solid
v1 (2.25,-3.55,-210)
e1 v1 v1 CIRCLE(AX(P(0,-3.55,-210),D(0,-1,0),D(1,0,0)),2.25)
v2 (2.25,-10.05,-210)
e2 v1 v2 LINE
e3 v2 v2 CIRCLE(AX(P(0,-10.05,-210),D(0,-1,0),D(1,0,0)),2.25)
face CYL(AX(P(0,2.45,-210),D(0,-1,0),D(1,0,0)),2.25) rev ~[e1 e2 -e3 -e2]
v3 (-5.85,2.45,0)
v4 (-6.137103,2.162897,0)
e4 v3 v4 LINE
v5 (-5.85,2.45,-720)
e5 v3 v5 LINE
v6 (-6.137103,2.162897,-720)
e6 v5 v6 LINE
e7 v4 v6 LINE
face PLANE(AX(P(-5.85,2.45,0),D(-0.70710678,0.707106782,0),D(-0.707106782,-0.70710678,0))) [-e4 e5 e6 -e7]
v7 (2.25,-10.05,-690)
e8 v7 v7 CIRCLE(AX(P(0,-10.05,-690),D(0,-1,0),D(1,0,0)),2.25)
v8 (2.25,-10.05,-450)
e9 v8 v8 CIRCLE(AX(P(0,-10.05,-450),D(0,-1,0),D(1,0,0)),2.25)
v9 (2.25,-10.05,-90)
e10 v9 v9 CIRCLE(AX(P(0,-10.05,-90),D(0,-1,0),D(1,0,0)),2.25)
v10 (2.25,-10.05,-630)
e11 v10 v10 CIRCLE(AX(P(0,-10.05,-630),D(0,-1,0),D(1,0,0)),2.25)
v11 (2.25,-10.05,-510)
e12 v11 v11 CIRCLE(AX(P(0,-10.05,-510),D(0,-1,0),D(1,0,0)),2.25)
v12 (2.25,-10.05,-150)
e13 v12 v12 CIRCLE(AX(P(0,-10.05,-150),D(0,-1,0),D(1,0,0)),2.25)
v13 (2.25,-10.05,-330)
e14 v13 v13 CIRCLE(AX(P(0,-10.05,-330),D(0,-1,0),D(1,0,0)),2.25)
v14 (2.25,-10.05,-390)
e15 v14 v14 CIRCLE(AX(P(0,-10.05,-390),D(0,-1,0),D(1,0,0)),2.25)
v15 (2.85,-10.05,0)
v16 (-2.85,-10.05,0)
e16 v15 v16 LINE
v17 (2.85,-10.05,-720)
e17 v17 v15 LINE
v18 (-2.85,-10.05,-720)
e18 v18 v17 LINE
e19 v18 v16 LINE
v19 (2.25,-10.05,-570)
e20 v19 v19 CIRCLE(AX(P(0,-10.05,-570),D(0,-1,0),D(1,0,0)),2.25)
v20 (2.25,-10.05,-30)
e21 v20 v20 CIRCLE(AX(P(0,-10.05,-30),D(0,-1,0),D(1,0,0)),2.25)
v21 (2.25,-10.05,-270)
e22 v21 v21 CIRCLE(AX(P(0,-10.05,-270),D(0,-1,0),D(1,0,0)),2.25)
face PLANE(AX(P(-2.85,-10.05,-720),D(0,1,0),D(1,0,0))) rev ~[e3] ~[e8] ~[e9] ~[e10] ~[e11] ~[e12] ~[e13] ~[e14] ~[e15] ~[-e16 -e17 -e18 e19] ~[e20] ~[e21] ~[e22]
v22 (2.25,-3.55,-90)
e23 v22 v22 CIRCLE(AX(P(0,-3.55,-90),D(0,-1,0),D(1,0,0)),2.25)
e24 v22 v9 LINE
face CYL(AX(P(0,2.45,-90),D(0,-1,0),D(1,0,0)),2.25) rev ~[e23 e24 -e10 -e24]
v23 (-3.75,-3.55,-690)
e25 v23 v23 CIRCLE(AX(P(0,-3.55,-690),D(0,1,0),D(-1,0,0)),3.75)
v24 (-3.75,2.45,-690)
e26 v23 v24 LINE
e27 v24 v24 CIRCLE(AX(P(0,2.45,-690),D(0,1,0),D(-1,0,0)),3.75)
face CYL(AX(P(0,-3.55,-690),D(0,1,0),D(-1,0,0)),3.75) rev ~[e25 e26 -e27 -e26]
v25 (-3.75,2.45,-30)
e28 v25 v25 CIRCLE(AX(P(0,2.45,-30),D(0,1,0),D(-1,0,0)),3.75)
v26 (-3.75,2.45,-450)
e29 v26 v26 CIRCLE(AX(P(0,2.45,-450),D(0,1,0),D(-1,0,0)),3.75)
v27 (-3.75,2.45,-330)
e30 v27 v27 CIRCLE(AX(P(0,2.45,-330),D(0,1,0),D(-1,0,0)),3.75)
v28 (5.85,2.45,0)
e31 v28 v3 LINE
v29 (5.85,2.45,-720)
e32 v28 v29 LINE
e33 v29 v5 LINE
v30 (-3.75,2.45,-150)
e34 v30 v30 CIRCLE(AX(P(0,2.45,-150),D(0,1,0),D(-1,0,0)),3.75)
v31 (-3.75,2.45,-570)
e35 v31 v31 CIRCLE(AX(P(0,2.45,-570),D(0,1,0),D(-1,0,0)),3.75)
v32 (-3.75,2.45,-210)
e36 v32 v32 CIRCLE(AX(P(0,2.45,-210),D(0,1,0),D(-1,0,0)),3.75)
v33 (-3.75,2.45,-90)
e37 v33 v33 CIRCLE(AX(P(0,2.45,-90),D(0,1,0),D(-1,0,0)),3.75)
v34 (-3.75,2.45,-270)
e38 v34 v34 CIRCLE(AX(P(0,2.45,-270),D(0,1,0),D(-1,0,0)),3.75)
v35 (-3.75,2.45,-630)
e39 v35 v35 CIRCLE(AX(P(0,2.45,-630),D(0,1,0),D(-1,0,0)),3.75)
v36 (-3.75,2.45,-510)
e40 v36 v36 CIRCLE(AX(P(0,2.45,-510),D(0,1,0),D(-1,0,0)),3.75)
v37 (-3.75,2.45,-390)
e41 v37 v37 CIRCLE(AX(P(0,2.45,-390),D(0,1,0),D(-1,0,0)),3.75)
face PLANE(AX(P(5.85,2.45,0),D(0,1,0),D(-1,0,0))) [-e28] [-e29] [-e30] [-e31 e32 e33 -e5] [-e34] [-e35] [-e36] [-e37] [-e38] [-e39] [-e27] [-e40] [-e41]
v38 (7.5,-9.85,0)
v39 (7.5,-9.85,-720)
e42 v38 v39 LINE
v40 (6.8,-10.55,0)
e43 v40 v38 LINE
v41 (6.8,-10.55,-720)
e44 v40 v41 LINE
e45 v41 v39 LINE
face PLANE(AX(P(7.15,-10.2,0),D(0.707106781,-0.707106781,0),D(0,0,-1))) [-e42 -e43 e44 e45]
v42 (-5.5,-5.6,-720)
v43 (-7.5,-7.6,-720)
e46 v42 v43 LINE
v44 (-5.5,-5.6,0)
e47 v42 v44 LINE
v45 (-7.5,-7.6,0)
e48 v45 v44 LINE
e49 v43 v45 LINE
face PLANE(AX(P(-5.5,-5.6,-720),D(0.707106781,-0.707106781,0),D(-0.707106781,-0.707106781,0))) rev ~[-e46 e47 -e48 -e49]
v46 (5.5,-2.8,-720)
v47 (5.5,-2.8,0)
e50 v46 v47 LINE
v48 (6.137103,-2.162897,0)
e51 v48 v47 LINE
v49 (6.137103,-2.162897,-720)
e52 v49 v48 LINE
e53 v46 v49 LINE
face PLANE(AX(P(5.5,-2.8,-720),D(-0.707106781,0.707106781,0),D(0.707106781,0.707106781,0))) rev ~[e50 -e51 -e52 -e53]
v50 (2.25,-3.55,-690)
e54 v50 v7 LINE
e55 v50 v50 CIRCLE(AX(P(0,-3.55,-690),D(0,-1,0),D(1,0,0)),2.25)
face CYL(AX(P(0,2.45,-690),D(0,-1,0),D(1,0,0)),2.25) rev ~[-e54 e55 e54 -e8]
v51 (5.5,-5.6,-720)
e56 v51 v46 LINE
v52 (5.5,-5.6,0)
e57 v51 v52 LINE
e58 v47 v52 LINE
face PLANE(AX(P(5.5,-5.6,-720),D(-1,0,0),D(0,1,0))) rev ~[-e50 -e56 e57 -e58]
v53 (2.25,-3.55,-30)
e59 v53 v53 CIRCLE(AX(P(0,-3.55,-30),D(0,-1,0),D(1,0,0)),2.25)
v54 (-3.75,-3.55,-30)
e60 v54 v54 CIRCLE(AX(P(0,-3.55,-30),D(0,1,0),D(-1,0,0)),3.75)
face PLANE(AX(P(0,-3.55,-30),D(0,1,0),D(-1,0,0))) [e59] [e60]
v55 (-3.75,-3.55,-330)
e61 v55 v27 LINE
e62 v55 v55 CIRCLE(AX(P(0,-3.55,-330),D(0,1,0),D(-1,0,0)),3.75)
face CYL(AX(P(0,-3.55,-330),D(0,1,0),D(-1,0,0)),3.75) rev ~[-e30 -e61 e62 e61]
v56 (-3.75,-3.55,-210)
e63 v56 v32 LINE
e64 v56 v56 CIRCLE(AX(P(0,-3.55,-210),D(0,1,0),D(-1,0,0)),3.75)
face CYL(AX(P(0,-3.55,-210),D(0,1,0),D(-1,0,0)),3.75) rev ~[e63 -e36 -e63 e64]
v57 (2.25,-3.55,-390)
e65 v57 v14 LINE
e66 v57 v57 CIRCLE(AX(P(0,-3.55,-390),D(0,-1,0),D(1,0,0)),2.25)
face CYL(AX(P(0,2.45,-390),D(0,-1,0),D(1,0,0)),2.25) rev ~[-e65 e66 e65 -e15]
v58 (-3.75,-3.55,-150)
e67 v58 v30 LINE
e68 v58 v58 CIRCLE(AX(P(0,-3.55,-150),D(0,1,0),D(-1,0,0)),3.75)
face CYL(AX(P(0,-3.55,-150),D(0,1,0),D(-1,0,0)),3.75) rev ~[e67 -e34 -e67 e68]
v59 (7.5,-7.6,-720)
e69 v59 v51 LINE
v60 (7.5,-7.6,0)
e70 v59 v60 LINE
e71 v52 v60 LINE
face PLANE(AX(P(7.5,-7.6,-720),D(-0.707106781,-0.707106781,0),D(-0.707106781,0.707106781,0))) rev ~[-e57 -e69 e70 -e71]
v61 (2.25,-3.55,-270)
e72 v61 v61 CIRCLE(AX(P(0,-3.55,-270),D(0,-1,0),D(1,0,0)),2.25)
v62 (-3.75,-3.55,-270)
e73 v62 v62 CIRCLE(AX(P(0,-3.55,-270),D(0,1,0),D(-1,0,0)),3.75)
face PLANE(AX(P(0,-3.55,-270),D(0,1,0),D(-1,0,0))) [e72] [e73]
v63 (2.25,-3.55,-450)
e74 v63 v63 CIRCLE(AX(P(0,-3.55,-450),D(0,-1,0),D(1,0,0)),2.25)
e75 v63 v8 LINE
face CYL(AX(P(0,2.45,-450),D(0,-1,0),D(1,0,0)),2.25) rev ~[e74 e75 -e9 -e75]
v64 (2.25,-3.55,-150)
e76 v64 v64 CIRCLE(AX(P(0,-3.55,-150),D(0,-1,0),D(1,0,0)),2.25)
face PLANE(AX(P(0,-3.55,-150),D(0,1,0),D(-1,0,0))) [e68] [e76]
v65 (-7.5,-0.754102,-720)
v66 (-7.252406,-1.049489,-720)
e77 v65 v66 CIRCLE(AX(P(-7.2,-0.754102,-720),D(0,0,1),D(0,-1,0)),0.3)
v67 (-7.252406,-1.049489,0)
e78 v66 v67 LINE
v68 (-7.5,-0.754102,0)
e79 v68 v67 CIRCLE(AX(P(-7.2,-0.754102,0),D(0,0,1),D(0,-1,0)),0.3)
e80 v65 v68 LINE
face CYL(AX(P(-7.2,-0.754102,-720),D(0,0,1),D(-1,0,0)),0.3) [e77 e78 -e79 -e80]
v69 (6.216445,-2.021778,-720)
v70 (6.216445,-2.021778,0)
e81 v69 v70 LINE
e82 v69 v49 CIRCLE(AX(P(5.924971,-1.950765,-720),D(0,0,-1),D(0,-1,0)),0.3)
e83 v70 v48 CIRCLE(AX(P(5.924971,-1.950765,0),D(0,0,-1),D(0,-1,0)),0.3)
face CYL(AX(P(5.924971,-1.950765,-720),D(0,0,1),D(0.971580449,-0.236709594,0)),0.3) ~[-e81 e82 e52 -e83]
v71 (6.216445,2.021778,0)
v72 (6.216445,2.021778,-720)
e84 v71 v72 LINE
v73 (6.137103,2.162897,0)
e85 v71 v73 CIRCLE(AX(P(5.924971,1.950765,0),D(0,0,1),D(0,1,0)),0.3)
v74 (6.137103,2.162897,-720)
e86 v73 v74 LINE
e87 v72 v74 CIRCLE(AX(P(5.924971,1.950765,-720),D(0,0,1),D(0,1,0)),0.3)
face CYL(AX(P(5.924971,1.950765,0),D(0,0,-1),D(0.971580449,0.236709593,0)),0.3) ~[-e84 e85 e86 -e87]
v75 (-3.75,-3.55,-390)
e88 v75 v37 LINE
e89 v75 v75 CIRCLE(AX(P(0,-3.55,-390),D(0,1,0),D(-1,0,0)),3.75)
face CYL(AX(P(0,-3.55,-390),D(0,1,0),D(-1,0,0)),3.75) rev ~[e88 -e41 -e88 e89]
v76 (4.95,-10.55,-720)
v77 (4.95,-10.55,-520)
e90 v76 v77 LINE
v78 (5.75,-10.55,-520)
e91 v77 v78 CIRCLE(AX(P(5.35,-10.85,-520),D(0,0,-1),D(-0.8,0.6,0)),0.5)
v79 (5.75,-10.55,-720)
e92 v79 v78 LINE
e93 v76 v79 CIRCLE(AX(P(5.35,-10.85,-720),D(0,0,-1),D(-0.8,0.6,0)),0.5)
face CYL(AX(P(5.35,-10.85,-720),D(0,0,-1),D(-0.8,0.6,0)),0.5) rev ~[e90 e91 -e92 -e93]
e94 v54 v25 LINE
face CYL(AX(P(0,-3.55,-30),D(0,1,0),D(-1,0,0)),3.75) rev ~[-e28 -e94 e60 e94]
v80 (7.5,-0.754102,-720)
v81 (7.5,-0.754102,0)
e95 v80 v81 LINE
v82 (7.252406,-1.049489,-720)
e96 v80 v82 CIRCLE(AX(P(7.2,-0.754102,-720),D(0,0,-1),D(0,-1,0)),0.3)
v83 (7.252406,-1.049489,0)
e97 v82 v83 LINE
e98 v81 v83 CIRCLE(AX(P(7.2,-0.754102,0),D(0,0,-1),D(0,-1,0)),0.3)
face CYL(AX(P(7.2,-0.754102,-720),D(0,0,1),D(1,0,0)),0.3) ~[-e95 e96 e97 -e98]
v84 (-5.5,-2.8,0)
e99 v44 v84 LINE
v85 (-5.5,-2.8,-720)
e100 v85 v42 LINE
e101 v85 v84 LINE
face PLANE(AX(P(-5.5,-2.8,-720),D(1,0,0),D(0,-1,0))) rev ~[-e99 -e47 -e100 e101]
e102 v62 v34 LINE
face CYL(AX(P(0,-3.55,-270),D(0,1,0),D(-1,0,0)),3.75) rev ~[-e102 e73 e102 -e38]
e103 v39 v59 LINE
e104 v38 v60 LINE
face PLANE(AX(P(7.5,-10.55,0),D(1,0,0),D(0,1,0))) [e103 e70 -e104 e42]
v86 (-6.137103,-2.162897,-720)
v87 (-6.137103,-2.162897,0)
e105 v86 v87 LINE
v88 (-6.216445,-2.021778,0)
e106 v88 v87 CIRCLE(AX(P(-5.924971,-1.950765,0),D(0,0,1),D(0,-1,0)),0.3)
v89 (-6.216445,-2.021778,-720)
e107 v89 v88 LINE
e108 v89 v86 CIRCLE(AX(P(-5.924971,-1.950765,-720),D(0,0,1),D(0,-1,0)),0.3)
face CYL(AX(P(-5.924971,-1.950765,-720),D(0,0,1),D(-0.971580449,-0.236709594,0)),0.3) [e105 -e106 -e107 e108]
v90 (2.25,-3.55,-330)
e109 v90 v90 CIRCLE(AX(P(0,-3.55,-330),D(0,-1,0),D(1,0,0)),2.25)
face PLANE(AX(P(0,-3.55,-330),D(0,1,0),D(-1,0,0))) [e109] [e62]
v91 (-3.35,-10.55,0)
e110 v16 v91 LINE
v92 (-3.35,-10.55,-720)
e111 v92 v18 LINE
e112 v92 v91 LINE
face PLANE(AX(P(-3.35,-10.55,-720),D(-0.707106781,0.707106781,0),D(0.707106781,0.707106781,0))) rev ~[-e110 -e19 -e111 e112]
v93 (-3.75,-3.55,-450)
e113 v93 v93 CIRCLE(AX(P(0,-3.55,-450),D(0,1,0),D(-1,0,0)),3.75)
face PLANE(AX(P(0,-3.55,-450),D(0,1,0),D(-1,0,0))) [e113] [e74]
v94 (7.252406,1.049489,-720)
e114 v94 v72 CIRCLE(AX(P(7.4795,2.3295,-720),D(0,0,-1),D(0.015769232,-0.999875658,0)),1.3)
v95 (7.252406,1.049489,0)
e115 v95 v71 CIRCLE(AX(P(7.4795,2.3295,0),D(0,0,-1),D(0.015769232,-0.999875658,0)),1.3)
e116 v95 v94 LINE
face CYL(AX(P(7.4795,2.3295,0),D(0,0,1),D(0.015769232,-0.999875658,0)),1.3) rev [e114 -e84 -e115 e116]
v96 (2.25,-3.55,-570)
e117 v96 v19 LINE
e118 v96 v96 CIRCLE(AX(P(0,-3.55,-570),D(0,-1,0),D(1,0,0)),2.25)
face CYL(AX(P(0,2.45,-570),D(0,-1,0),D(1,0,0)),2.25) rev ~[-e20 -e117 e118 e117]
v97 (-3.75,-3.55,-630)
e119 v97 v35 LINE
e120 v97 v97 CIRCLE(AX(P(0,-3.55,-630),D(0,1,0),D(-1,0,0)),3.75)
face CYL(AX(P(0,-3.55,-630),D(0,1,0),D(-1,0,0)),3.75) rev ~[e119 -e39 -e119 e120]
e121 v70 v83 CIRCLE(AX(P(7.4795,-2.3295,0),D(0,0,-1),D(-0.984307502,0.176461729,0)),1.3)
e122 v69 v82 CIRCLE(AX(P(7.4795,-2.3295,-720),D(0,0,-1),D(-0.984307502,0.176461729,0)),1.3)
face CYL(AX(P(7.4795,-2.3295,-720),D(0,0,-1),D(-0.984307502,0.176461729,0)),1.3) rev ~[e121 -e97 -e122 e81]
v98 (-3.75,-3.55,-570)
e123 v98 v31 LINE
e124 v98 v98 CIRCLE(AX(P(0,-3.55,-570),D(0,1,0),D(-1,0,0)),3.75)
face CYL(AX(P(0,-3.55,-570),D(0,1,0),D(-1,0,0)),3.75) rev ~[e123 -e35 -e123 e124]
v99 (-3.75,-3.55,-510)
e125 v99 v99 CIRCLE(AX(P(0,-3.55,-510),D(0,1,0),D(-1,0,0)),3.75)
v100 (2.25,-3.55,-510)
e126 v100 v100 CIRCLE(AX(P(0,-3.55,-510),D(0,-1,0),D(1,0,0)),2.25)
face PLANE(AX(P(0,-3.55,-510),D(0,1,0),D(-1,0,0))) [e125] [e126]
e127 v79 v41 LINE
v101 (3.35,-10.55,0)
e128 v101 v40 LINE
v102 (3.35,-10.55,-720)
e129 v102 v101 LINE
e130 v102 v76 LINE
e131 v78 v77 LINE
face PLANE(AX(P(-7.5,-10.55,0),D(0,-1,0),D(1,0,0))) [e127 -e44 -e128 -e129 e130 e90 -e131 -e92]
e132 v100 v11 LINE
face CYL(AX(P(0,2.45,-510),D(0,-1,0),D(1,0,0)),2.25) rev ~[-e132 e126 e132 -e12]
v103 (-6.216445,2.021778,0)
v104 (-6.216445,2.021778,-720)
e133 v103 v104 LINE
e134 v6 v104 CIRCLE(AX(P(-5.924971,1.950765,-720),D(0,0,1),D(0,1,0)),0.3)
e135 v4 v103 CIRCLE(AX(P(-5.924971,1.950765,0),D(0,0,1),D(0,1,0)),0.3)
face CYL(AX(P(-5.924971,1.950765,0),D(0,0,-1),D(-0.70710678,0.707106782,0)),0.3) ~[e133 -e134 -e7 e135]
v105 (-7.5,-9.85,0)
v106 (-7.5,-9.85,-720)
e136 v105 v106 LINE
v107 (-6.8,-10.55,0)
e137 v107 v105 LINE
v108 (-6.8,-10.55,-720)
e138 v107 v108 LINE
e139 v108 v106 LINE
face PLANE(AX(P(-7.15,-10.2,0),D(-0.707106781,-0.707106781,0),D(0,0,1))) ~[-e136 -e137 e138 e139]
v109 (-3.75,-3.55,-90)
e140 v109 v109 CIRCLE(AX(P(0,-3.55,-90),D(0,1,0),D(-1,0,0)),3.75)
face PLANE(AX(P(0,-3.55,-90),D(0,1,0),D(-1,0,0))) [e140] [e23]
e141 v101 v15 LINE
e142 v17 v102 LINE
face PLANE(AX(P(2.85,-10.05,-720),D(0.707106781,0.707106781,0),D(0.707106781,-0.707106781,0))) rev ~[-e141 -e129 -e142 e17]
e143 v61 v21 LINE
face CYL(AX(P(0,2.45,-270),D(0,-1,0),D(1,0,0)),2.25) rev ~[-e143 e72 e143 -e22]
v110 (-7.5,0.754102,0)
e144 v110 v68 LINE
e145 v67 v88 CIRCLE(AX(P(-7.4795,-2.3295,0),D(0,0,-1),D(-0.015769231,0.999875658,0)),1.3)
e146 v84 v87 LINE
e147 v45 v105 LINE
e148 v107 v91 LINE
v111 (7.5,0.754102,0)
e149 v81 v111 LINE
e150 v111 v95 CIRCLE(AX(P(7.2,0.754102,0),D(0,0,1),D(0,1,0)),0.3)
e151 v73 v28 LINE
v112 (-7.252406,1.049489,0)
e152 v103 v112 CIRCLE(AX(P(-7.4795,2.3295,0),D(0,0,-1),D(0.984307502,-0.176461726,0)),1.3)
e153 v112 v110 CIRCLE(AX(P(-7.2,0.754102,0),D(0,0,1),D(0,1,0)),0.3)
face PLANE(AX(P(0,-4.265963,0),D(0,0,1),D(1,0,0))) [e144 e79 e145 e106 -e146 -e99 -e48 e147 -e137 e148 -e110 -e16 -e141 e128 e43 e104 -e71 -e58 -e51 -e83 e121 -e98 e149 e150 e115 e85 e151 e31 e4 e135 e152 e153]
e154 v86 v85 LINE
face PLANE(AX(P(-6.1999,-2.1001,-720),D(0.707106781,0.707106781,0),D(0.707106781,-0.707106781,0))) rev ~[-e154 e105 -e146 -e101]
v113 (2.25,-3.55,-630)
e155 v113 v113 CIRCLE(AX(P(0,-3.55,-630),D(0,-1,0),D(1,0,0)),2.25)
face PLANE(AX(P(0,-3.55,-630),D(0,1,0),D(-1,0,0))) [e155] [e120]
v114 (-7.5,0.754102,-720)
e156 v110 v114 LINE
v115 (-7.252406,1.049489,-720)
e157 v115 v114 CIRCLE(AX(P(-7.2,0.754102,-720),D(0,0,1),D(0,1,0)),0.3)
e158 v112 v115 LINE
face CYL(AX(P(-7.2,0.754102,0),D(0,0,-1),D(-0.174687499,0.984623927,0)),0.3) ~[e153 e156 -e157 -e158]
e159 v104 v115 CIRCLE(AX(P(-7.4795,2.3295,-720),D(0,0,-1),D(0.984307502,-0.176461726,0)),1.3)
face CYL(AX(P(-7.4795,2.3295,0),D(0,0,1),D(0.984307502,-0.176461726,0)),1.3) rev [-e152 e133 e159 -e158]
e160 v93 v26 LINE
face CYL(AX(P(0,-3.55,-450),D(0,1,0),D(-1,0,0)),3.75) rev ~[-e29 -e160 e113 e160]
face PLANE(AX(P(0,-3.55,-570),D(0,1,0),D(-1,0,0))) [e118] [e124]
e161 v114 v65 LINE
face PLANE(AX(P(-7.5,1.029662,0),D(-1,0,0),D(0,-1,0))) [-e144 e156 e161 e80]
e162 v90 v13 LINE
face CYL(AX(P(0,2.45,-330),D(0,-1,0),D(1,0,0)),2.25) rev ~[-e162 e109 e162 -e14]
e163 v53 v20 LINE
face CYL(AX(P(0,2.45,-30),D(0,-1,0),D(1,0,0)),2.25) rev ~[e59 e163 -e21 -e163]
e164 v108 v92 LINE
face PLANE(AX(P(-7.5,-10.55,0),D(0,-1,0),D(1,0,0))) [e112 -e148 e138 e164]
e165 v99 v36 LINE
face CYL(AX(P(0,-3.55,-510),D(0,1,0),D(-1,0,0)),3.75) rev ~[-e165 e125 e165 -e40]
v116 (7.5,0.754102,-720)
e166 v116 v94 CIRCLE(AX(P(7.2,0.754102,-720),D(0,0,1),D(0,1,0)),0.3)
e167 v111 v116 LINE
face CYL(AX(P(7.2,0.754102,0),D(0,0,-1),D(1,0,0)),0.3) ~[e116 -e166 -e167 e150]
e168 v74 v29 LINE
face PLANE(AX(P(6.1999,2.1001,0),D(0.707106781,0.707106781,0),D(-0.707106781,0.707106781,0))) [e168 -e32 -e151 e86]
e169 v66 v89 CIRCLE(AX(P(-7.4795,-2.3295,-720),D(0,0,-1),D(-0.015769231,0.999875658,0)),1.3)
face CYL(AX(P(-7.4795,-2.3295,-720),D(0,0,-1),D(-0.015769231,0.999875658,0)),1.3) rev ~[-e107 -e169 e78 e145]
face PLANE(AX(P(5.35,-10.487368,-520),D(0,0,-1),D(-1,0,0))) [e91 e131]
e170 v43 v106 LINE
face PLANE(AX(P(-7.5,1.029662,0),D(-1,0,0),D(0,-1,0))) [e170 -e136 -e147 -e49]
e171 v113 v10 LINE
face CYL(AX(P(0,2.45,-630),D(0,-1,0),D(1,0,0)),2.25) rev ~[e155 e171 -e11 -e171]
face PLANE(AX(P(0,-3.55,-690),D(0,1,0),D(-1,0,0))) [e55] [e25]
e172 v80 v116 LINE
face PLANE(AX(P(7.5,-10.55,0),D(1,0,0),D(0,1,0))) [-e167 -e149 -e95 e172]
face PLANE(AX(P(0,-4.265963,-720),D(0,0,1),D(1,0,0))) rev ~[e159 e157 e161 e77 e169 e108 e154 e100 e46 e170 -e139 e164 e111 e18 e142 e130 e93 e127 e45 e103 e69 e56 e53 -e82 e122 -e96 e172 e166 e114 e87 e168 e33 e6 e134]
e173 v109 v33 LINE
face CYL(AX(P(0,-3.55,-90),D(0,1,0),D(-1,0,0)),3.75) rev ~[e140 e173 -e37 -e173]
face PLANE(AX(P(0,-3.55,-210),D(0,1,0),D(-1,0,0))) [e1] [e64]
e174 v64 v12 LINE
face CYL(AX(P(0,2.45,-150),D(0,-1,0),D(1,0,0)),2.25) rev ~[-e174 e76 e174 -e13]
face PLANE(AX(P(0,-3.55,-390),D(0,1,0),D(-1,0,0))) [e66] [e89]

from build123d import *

# Parameters (mm, degrees)
BOSS_EXTRUDE1_DEPTH = 720
CUT_EXTRUDE1_DEPTH  = 721.116346502
CUT_EXTRUDE2_DEPTH  = 721.116346502
CUT_EXTRUDE3_DEPTH  = 721.116346502
CUT_EXTRUDE4_DEPTH  = 200
HOLE1_D             = 4.5
HOLE1_CBORE_D       = 7.5
HOLE1_CBORE_DEPTH   = 6
CHAMFER1_SIZE       = 0.7
CHAMFER2_SIZE       = 0.7
FILLET1_R           = 0.3
FILLET2_R           = 0.3
FILLET3_R           = 0.3
FILLET4_R           = 0.3
FILLET5_R           = 0.3
FILLET6_R           = 0.3
FILLET7_R           = 0.3
FILLET8_R           = 0.3
LPATTERN1_COUNT     = 12
LPATTERN1_PITCH     = 60


with BuildPart() as part:
    # Sketch1 → Boss-Extrude1 (new body)
    with BuildSketch(Plane.XY):
        with BuildLine():
            Line((7.5, -10.55), (7.5, 1.029661645))
            ThreePointArc((7.5, 1.029661645), (6.653187418, 1.325902711), (6.199900247, 2.100099753))
            Line((6.199900247, 2.100099753), (5.85, 2.45))
            Line((5.85, 2.45), (-5.85, 2.45))
            Line((-5.85, 2.45), (-6.199900248, 2.100099753))
            ThreePointArc((-6.199900248, 2.100099753), (-6.653187418, 1.325902711), (-7.5, 1.029661645))
            Line((-7.5, 1.029661645), (-7.5, -10.55))
            Line((-7.5, -10.55), (7.5, -10.55))
        make_face()
    extrude(amount=-BOSS_EXTRUDE1_DEPTH)

    # Sketch2 → Cut-Extrude1 (cut, through all)
    with BuildSketch(Plane(origin=(0, 0, -720), x_dir=(-1, 0, 0), z_dir=(0, 0, -1))):
        with BuildLine():
            Line((-7.5, -1.029661645), (-7.5, -7.6))
            Line((-7.5, -7.6), (-5.5, -5.6))
            Line((-5.5, -5.6), (-5.5, -2.8))
            Line((-5.5, -2.8), (-6.199900248, -2.100099752))
            ThreePointArc((-6.199900248, -2.100099752), (-6.653187419, -1.325902711), (-7.5, -1.029661645))
        make_face()
    extrude(amount=-CUT_EXTRUDE1_DEPTH, mode=Mode.SUBTRACT)

    # Sketch3 → Cut-Extrude2 (cut, through all)
    with BuildSketch(Plane(origin=(0, 0, -720), x_dir=(-1, 0, 0), z_dir=(0, 0, -1))):
        with BuildLine():
            Line((6.199900248, -2.100099752), (5.5, -2.8))
            Line((5.5, -2.8), (5.5, -5.6))
            Line((5.5, -5.6), (7.5, -7.6))
            Line((7.5, -7.6), (7.5, -1.029661645))
            ThreePointArc((7.5, -1.029661645), (6.653187419, -1.325902711), (6.199900248, -2.100099752))
        make_face()
    extrude(amount=-CUT_EXTRUDE2_DEPTH, mode=Mode.SUBTRACT)

    # Sketch4 → Cut-Extrude3 (cut, through all)
    with BuildSketch(Plane(origin=(0, 0, -720), x_dir=(-1, 0, 0), z_dir=(0, 0, -1))):
        Polygon((-3.35, -10.55), (3.35, -10.55), (2.85, -10.05), (-2.85, -10.05), align=None)
    extrude(amount=-CUT_EXTRUDE3_DEPTH, mode=Mode.SUBTRACT)

    # Sketch5 → Cut-Extrude4 (cut)
    with BuildSketch(Plane(origin=(0, 0, -720), x_dir=(-1, 0, 0), z_dir=(0, 0, -1))):
        with BuildLine():
            Line((-5.75, -10.55), (-4.95, -10.55))
            ThreePointArc((-4.95, -10.55), (-5.35, -10.35), (-5.75, -10.55))
        make_face()
    extrude(amount=-CUT_EXTRUDE4_DEPTH, mode=Mode.SUBTRACT)

    # Hole1 (through all)
    with Locations(Plane(origin=(0, 2.45, 0), x_dir=(-1, 0, 0), z_dir=(0, 1, 0))):
        with Locations((0, -30)):
            hole1 = CounterBoreHole(HOLE1_D / 2, HOLE1_CBORE_D / 2, HOLE1_CBORE_DEPTH)

    # Chamfer1
    chamfer1_edges = [part.edges().sort_by_distance(p)[0] for p in [
        (-7.5, -10.55, -360),
    ]]
    chamfer(chamfer1_edges, length=CHAMFER1_SIZE)

    # Chamfer2
    chamfer2_edges = [part.edges().sort_by_distance(p)[0] for p in [
        (7.5, -10.55, -360),
    ]]
    chamfer(chamfer2_edges, length=CHAMFER2_SIZE)

    # Fillet1
    fillet1_edges = [part.edges().sort_by_distance(p)[0] for p in [
        (7.5, 1.029661645, -360),
    ]]
    fillet(fillet1_edges, radius=FILLET1_R)

    # Fillet2
    fillet2_edges = [part.edges().sort_by_distance(p)[0] for p in [
        (-7.5, 1.029661645, -360),
    ]]
    fillet(fillet2_edges, radius=FILLET2_R)

    # Fillet3
    fillet3_edges = [part.edges().sort_by_distance(p)[0] for p in [
        (7.5, -1.029661645, -360),
    ]]
    fillet(fillet3_edges, radius=FILLET3_R)

    # Fillet4
    fillet4_edges = [part.edges().sort_by_distance(p)[0] for p in [
        (6.199900247, 2.100099753, -360),
    ]]
    fillet(fillet4_edges, radius=FILLET4_R)

    # Fillet5
    fillet5_edges = [part.edges().sort_by_distance(p)[0] for p in [
        (-7.5, -1.029661645, -360),
    ]]
    fillet(fillet5_edges, radius=FILLET5_R)

    # Fillet6
    fillet6_edges = [part.edges().sort_by_distance(p)[0] for p in [
        (-6.199900248, -2.100099752, -360),
    ]]
    fillet(fillet6_edges, radius=FILLET6_R)

    # Fillet7
    fillet7_edges = [part.edges().sort_by_distance(p)[0] for p in [
        (6.199900248, -2.100099752, -360),
    ]]
    fillet(fillet7_edges, radius=FILLET7_R)

    # Fillet8
    fillet8_edges = [part.edges().sort_by_distance(p)[0] for p in [
        (-6.199900248, 2.100099753, -360),
    ]]
    fillet(fillet8_edges, radius=FILLET8_R)

    # LPattern1: Hole1 ×12
    with Locations(*[(0, 0, -i * LPATTERN1_PITCH) for i in range(1, LPATTERN1_COUNT)]):
        add(hole1, mode=Mode.SUBTRACT)


solid = part.part
